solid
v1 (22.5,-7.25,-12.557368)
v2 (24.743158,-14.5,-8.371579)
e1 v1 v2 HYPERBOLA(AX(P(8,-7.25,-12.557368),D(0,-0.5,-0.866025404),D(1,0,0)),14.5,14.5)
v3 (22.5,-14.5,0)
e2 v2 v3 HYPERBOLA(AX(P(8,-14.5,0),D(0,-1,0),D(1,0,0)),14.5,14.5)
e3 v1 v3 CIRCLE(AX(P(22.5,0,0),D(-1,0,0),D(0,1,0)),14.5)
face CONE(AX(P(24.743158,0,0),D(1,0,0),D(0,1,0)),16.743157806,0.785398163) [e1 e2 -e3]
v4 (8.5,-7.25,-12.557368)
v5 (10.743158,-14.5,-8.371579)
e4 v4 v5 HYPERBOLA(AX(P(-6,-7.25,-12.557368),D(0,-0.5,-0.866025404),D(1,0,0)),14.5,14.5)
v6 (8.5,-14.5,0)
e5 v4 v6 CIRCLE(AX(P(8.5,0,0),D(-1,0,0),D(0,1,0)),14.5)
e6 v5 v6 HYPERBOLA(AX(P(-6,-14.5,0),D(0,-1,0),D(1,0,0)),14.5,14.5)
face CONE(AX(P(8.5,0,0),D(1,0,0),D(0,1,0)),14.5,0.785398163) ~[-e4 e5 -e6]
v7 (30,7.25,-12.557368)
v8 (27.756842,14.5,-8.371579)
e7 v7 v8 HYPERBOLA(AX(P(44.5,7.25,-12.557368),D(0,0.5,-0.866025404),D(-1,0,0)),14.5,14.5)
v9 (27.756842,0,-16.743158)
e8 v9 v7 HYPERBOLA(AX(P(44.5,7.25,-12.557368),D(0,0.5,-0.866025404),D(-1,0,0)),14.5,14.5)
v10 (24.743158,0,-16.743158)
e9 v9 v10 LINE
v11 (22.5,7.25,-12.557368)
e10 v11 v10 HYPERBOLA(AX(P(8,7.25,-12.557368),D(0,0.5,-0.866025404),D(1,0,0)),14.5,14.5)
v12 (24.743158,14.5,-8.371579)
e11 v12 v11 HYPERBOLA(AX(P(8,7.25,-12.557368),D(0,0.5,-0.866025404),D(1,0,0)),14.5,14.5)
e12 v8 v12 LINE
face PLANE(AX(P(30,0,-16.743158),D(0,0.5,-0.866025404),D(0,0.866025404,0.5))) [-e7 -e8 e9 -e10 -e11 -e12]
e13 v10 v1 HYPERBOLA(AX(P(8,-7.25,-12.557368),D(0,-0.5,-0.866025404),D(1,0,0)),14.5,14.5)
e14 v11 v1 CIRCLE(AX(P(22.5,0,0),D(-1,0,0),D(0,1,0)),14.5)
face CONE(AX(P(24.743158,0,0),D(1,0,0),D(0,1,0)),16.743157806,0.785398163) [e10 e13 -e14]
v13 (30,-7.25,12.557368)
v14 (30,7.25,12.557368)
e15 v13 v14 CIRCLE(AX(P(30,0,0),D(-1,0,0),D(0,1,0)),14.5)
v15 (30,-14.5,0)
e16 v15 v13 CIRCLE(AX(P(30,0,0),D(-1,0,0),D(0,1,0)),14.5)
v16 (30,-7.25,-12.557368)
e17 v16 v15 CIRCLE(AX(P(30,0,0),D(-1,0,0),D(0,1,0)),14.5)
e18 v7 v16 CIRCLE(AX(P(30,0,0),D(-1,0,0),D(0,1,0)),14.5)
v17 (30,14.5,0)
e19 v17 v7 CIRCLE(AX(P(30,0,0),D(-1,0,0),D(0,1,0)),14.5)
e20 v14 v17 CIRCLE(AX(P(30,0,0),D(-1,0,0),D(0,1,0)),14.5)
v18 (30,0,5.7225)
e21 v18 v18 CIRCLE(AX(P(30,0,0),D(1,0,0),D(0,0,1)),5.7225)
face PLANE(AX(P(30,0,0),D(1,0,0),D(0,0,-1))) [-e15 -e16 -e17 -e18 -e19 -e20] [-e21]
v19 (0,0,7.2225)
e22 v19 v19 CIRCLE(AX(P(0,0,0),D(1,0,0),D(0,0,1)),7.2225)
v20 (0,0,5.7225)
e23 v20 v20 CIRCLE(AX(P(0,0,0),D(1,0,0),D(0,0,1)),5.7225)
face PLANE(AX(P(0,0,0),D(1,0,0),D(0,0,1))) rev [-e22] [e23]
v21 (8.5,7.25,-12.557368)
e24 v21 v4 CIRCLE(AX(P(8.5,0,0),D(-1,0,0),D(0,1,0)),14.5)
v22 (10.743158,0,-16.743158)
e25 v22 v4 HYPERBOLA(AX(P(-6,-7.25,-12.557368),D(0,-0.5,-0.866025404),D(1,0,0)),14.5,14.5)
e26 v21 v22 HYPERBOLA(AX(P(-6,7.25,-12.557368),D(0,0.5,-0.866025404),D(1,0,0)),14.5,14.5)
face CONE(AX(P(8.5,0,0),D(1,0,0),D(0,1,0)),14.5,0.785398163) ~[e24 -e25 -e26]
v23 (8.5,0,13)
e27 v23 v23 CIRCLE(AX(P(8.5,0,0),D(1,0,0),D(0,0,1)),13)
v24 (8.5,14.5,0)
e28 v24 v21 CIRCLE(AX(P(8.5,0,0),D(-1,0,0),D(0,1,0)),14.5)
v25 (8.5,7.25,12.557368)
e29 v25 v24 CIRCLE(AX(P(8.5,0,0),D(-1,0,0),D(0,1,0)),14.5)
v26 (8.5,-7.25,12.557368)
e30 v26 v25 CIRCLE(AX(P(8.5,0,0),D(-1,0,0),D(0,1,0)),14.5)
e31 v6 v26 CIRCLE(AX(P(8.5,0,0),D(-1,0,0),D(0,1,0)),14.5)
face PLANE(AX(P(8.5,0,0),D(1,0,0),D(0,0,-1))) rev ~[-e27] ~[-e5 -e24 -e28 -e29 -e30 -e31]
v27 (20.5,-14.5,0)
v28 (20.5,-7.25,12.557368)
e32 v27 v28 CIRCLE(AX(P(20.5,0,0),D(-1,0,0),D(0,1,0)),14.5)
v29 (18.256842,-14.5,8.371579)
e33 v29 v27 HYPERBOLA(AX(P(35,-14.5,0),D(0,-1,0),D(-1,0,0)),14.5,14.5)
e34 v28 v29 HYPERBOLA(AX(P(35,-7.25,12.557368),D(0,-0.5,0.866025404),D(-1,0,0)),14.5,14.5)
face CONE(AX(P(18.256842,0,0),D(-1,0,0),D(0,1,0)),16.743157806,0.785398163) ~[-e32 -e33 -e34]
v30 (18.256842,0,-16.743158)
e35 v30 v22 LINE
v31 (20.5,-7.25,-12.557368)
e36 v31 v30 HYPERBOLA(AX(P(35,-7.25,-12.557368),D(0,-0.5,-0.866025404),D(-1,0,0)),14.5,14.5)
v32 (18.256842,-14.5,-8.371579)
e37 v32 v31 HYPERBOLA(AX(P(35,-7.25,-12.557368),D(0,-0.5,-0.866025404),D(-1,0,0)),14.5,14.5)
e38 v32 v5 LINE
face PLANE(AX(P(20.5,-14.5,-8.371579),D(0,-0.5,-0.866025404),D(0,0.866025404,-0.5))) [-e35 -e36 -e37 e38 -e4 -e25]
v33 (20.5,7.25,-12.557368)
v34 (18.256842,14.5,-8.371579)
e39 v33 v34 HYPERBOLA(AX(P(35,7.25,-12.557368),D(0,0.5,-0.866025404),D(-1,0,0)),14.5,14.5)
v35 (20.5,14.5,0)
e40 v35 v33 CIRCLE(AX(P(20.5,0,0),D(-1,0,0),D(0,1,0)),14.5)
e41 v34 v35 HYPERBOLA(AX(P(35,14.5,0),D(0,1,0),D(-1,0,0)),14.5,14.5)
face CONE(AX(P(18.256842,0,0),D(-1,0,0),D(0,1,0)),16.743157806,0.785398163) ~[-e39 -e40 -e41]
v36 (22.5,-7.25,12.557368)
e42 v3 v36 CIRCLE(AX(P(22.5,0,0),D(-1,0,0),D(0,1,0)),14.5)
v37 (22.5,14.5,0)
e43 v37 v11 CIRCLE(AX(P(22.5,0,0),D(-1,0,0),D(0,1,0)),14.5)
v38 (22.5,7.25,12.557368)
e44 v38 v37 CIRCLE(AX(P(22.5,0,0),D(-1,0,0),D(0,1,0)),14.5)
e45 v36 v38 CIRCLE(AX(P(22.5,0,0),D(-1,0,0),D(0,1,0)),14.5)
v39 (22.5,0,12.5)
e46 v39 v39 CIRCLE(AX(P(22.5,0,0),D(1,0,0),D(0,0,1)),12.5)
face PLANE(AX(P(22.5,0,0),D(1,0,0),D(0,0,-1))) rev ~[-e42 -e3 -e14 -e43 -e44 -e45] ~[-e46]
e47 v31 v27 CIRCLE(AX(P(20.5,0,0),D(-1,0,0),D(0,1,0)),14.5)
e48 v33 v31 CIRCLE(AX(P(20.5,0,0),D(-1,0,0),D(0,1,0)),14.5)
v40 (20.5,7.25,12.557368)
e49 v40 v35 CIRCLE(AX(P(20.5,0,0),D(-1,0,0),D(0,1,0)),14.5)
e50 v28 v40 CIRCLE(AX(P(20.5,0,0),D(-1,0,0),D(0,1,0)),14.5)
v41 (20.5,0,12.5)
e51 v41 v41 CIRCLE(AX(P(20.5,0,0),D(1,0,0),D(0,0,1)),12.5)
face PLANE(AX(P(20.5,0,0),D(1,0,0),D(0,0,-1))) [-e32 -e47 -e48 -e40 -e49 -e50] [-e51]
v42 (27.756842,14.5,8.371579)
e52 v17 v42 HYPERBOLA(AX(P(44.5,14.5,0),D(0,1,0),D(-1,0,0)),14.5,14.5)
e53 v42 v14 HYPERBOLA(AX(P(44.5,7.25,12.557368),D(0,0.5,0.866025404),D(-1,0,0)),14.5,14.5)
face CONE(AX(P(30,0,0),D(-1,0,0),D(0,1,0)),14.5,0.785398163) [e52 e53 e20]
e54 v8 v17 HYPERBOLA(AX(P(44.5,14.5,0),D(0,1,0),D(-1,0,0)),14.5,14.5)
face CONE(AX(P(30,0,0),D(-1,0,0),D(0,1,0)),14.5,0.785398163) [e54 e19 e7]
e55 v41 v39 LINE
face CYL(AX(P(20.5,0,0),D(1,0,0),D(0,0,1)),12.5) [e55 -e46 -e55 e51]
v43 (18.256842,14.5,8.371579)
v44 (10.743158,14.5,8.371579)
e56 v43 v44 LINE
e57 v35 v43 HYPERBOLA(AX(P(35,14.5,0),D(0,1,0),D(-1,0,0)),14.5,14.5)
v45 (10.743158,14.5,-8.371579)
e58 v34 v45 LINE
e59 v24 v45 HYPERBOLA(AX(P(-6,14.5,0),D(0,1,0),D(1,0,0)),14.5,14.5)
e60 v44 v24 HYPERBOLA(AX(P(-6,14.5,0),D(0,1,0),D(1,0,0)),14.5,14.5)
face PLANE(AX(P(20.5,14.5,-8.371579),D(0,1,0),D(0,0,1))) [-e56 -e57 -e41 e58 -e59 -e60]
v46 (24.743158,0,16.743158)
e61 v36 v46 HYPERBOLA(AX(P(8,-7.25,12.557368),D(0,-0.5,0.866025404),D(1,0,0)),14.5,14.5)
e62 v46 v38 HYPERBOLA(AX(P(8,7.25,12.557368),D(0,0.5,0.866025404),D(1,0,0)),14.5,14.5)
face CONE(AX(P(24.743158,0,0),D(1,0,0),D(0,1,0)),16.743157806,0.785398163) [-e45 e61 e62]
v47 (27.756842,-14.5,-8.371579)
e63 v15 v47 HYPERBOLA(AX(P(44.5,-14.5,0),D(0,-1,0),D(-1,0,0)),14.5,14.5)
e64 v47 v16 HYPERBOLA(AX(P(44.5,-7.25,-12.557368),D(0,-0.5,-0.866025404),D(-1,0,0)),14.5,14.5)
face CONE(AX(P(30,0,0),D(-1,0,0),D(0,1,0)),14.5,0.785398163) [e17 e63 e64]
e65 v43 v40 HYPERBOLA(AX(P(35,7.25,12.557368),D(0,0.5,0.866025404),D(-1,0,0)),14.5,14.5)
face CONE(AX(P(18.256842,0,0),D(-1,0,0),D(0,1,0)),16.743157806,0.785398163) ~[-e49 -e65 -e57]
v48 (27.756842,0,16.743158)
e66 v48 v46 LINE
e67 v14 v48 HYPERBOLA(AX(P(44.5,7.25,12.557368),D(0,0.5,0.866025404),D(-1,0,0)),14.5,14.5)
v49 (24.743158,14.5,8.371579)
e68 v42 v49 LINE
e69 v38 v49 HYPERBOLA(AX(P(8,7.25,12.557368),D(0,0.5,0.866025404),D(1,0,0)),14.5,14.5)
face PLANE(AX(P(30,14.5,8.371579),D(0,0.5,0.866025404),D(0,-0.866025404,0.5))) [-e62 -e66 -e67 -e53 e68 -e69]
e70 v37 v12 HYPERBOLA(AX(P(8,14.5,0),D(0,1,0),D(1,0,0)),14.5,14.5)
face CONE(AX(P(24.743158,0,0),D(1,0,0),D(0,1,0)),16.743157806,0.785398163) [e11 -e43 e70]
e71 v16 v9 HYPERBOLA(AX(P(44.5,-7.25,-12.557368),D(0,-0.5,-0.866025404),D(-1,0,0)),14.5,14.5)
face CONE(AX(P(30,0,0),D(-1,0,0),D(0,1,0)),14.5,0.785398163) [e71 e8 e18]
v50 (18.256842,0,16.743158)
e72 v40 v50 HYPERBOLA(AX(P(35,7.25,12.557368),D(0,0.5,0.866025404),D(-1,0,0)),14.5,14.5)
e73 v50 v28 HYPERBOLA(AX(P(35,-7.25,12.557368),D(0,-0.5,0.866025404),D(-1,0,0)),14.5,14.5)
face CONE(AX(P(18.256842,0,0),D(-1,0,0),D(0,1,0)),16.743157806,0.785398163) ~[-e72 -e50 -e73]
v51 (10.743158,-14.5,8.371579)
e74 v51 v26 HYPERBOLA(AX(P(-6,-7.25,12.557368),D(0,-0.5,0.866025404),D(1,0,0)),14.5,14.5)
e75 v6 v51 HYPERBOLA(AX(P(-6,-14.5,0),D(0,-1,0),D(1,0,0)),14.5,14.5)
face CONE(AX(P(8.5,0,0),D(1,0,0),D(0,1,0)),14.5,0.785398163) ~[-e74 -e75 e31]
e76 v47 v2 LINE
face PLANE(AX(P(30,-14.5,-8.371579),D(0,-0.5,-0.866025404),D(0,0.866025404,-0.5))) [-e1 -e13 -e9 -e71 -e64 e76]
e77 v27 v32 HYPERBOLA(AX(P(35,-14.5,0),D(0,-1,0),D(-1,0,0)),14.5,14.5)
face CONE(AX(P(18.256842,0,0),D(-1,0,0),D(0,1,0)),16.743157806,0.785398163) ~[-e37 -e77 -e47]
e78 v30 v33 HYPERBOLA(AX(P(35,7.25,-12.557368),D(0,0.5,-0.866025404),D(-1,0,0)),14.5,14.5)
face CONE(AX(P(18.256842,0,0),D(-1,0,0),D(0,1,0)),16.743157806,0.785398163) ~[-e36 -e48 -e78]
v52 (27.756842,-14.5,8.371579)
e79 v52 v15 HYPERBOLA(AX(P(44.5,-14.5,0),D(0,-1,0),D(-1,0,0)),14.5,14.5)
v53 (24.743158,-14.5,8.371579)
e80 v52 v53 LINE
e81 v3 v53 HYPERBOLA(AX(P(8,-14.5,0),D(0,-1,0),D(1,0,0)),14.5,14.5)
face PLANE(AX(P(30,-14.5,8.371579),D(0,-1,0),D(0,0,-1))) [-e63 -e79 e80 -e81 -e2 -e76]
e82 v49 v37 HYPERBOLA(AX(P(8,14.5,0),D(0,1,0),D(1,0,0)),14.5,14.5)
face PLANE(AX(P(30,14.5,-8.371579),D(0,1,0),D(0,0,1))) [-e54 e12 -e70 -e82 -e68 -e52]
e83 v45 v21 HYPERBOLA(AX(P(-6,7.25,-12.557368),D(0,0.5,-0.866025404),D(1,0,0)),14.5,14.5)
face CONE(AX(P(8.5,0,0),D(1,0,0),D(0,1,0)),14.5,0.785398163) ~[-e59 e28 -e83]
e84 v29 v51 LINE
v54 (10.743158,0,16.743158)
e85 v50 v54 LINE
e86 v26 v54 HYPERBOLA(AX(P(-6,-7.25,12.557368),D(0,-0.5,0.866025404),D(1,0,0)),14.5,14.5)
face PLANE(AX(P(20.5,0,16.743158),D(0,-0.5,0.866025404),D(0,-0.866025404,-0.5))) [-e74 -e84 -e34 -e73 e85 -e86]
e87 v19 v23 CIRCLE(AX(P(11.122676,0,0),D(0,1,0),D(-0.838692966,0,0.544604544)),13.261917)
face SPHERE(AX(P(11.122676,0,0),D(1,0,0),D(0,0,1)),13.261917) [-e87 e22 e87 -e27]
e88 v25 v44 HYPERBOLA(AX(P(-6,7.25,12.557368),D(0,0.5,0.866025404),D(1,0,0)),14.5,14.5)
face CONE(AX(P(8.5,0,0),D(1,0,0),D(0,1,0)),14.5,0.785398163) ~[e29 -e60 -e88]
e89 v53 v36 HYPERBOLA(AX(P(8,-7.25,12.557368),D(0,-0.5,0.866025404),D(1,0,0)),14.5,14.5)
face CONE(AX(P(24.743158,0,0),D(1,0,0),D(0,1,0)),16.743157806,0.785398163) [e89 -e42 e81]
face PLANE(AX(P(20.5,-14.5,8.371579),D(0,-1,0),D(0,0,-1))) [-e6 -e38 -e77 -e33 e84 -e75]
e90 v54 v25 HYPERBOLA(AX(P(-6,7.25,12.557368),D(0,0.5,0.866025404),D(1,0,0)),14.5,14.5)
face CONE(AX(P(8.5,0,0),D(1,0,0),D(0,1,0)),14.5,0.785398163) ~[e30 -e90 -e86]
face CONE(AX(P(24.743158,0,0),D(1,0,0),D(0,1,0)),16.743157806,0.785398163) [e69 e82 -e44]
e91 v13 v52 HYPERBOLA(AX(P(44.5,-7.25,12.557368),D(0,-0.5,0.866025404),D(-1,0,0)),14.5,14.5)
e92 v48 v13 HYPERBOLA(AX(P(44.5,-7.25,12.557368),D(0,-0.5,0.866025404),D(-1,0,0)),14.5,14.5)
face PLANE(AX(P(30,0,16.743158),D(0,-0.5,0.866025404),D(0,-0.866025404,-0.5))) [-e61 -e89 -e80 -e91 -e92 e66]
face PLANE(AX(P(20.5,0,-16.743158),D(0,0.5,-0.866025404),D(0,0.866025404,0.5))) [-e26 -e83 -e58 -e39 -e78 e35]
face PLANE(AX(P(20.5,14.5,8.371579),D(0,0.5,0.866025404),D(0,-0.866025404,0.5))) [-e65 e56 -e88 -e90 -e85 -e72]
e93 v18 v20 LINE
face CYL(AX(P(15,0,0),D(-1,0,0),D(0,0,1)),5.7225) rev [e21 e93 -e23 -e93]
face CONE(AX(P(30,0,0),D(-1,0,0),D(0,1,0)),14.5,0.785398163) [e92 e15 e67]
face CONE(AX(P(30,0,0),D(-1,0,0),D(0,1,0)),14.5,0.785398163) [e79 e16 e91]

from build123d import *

# Parameters (mm, degrees)
SKETCH2_R           = 12.5
BOSS_EXTRUDE1_DEPTH = 12
SKETCH6_R           = 12.5
BOSS_EXTRUDE2_DEPTH = 7.5
SKETCH5_R           = 1
CUT_EXTRUDE2_DEPTH  = 27.750389405
CUT_EXTRUDE3_START  = -15
SKETCH7_R           = 5.7225
CUT_EXTRUDE3_DEPTH  = 15


with BuildPart() as part:
    # Sketch1 → Revolve1 (revolve)
    with BuildSketch(Plane.XY, mode=Mode.PRIVATE) as revolve1_sk:
        with BuildLine():
            Line((0, 5.7225), (0, 7.2225))
            ThreePointArc((0, 7.2225), (3.667573597, 10.968130039), (8.5, 13))
            Line((8.5, 13), (8.5, 14.5))
            Line((8.5, 14.5), (20.5, 14.5))
            Line((20.5, 14.5), (20.5, 12.5))
            Line((20.5, 12.5), (22.5, 12.5))
            Line((22.5, 12.5), (22.5, 14.5))
            Line((22.5, 14.5), (30, 14.5))
            Line((30, 14.5), (30, 0))
            Line((30, 0), (15, 0))
            Line((15, 0), (15, 5.7225))
            Line((15, 5.7225), (0, 5.7225))
        make_face()
    revolve(revolve1_sk.sketch.rotate(Axis((0, 0, 0), (1, 0, 0)), 90), axis=Axis((0, 0, 0), (1, 0, 0)))

    # Sketch2 → Boss-Extrude1 (add)
    with BuildSketch(Plane(origin=(20.5, 0, 0), x_dir=(0, 0, -1), z_dir=(1, 0, 0))):
        Polygon((16.743157806, 0), (8.371578903, 14.5), (-8.371578903, 14.5), (-16.743157806, 0), (-8.371578903, -14.5), (8.371578903, -14.5), align=None)
        with Locations(Location((0, 0, 0), (0, 0, 180))):
            Circle(SKETCH2_R, mode=Mode.SUBTRACT)
    extrude(amount=-BOSS_EXTRUDE1_DEPTH)

    # Sketch6 → Boss-Extrude2 (add)
    with BuildSketch(Plane(origin=(30, 0, 0), x_dir=(0, 0, -1), z_dir=(1, 0, 0))):
        Polygon((16.743157806, 0), (8.371578903, 14.5), (-8.371578903, 14.5), (-16.743157806, 0), (-8.371578903, -14.5), (8.371578903, -14.5), align=None)
        with Locations(Location((0, 0, 0), (0, 0, 180))):
            Circle(SKETCH6_R, mode=Mode.SUBTRACT)
    extrude(amount=-BOSS_EXTRUDE2_DEPTH)

    # Sketch3 → Cut-Revolve1 (revolve, cut)
    with BuildSketch(Plane(origin=(0, 0, 0), x_dir=(1, 0, 0), z_dir=(0, 1, 0)), mode=Mode.PRIVATE) as cut_revolve1_sk:
        Polygon((18.256842194, 16.743157806), (20.5, 14.5), (20.5, 16.743157806), align=None)
        Polygon((24.743157806, 16.743157806), (22.5, 14.5), (22.5, 16.743157806), align=None)
        Polygon((8.5, 14.5), (10.743157806, 16.743157806), (8.5, 16.743157806), align=None)
        Polygon((27.756842194, 16.743157806), (30, 16.743157806), (30, 14.5), align=None)
    revolve(cut_revolve1_sk.sketch.rotate(Axis((0, 0, 0), (-1, 0, 0)), 270), axis=Axis((0, 0, 0), (-1, 0, 0)), mode=Mode.SUBTRACT)

    # Sketch5 → Cut-Extrude2 (cut, through all)
    with BuildSketch(Plane.ZY.offset(-15)):
        Circle(SKETCH5_R)
    extrude(amount=-CUT_EXTRUDE2_DEPTH, mode=Mode.SUBTRACT)

    # Sketch7 → Cut-Extrude3 (cut)
    with BuildSketch(Plane(origin=(30, 0, 0), x_dir=(0, 0, -1), z_dir=(1, 0, 0)).offset(CUT_EXTRUDE3_START)):
        with Locations(Location((0, 0, 0), (0, 0, 180))):
            Circle(SKETCH7_R)
    extrude(amount=CUT_EXTRUDE3_DEPTH, mode=Mode.SUBTRACT)


solid = part.part
